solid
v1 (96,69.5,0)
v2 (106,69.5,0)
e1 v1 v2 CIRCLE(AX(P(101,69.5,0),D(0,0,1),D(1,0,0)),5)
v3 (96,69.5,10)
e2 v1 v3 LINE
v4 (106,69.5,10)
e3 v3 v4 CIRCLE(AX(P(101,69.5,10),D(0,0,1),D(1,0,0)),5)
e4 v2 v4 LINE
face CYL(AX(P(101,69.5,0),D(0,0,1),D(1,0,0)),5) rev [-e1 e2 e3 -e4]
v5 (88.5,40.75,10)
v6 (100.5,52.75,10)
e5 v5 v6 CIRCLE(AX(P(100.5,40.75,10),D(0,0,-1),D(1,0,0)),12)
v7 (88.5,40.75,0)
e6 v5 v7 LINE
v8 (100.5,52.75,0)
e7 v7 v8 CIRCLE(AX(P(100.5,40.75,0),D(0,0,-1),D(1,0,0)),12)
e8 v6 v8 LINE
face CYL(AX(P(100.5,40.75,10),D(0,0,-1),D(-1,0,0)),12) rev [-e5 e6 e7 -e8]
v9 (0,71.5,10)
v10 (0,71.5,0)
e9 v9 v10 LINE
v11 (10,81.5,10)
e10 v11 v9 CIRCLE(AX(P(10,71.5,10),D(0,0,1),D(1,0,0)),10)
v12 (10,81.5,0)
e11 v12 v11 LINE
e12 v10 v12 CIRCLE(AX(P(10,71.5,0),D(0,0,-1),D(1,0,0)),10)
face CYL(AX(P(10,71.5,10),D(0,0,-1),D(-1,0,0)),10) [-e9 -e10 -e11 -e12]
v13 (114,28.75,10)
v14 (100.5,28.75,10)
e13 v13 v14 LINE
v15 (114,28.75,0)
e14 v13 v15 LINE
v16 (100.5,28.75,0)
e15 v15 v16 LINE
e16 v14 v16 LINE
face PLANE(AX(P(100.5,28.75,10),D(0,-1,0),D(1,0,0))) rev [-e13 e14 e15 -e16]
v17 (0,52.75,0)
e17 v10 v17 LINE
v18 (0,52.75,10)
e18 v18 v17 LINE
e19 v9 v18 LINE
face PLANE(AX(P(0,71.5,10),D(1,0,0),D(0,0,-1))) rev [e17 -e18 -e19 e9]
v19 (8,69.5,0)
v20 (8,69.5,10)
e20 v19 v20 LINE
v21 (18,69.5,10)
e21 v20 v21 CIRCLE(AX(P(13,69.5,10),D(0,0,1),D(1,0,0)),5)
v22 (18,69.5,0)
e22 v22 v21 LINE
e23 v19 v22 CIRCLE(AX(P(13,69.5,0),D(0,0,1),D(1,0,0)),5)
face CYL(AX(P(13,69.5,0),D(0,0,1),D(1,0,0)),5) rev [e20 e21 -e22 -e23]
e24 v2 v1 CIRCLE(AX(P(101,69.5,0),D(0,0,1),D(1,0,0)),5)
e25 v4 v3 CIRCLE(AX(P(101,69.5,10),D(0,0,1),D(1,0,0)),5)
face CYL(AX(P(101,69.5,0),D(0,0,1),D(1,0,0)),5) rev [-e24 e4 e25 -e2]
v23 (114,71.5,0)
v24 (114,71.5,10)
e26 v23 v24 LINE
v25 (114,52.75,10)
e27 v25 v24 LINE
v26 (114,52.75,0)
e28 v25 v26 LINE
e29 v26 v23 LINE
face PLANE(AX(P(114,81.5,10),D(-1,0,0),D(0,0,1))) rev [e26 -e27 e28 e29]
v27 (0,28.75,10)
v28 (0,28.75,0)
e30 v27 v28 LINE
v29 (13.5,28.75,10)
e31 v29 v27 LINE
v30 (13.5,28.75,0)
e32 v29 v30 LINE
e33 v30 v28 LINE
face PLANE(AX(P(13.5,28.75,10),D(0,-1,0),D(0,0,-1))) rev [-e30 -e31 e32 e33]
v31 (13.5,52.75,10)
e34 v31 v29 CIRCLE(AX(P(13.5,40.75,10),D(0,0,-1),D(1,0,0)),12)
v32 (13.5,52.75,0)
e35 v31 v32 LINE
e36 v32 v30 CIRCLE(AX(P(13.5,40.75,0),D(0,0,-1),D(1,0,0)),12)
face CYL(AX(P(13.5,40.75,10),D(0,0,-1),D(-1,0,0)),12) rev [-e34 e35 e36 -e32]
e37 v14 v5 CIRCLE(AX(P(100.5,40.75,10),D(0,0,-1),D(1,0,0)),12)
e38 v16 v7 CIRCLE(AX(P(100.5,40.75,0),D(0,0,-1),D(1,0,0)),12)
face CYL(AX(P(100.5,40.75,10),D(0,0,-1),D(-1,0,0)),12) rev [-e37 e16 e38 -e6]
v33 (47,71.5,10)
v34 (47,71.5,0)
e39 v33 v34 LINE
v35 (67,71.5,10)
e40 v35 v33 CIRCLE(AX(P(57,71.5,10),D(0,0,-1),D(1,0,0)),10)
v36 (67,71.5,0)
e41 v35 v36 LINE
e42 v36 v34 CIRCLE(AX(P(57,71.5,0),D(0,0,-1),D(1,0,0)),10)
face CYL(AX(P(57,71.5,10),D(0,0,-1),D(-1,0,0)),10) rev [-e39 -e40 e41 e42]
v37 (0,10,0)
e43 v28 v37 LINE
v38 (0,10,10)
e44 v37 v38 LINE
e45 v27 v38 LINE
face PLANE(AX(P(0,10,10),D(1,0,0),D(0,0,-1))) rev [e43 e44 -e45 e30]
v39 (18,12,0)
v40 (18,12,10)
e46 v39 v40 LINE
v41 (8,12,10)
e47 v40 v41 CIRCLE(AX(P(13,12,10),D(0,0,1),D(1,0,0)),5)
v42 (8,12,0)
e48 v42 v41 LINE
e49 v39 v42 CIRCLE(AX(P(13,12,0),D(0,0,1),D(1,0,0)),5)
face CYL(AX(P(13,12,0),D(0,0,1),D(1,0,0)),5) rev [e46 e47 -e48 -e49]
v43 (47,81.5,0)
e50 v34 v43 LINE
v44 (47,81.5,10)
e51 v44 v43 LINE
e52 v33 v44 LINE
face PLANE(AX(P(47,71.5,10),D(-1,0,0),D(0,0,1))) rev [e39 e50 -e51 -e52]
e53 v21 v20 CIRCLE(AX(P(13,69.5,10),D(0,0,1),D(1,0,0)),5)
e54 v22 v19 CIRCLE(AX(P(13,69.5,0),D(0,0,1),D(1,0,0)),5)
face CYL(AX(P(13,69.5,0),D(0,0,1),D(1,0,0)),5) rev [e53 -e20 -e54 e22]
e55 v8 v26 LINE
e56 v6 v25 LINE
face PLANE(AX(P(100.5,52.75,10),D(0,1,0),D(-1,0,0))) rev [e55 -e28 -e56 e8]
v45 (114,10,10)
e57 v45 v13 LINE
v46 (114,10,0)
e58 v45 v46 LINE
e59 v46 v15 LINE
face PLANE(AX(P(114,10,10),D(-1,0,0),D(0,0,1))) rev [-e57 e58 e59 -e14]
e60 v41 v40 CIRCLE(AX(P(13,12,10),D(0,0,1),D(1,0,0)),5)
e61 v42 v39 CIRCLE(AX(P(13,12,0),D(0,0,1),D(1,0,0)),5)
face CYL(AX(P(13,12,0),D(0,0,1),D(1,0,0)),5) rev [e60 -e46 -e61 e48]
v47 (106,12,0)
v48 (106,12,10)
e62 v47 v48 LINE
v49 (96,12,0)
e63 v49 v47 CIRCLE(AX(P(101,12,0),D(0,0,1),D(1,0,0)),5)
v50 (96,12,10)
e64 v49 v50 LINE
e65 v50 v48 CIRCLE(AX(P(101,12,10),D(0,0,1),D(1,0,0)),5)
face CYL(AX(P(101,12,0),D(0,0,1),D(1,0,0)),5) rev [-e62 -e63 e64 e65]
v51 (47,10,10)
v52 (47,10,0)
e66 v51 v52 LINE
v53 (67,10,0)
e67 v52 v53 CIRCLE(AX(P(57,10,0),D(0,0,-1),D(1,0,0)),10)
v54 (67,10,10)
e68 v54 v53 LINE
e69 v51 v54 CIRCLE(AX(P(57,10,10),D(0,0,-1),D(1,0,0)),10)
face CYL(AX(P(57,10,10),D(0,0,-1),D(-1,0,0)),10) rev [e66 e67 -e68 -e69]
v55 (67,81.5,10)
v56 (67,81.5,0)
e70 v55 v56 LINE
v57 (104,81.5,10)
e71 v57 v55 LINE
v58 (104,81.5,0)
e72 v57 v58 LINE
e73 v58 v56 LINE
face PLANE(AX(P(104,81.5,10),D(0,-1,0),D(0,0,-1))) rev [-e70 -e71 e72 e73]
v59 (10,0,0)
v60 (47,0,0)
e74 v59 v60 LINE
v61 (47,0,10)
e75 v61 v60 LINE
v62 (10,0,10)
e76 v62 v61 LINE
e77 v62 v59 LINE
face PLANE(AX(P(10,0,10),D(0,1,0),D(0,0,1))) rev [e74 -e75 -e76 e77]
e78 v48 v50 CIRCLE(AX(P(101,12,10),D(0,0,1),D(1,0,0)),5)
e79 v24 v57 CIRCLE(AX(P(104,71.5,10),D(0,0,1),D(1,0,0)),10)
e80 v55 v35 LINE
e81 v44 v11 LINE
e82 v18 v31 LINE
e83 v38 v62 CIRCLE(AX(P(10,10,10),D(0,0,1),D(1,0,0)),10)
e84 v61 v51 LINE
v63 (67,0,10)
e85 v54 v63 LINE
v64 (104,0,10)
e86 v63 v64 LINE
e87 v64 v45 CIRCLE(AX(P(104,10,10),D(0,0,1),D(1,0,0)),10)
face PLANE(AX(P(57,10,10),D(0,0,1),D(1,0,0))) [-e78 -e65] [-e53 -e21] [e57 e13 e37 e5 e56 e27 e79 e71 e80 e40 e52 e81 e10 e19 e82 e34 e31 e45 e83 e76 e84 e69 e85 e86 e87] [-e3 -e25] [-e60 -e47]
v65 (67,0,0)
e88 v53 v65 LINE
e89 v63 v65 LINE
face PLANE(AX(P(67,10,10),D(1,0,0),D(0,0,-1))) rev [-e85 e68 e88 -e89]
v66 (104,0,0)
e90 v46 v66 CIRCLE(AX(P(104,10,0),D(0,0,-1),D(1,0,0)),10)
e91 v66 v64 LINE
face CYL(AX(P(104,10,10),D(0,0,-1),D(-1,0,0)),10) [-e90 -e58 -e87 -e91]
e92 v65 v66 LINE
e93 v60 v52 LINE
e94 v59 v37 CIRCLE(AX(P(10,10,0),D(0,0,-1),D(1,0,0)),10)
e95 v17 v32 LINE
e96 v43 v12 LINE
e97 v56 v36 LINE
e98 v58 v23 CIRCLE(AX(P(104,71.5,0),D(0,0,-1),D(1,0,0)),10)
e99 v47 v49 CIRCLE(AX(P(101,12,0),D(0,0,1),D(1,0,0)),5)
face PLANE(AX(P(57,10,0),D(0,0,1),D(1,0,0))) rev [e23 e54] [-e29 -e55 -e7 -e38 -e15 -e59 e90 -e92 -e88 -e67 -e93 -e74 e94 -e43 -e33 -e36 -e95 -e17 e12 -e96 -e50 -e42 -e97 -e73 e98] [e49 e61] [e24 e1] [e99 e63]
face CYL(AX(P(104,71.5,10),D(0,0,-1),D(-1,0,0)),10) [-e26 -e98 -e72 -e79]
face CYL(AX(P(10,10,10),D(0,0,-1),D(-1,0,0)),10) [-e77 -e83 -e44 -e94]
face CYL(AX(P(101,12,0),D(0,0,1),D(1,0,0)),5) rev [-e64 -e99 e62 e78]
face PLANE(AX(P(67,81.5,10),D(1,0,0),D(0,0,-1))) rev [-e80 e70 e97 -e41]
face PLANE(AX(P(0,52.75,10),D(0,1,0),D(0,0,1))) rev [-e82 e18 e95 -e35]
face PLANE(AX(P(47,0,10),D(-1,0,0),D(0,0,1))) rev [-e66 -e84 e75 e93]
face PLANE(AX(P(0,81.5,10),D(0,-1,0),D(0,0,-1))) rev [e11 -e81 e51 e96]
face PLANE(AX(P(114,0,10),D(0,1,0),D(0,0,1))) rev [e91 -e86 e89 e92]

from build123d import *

# Parameters (mm, degrees)
BRACKET_PLATE_DEPTH        = 10
MOUNTING_HOLES_SKETCH_R    = 5
MOUNTING_HOLES_4X_10_DEPTH = 141.492882382
CORNER_FILLETS_R10_R       = 10


with BuildPart() as part:
    # Bracket Profile Sketch → Bracket Plate (new body)
    with BuildSketch(Plane.XY):
        with BuildLine():
            Line((10, 0), (47, 0))
            Line((47, 0), (47, 10))
            ThreePointArc((47, 10), (57, 20), (67, 10))
            Line((67, 10), (67, 0))
            Line((67, 0), (104, 0))
            Line((104, 0), (114, 0))
            Line((114, 0), (114, 10))
            Line((114, 10), (114, 28.75))
            Line((114, 28.75), (100.5, 28.75))
            ThreePointArc((100.5, 28.75), (88.5, 40.75), (100.5, 52.75))
            Line((100.5, 52.75), (114, 52.75))
            Line((114, 52.75), (114, 71.5))
            Line((114, 71.5), (114, 81.5))
            Line((114, 81.5), (104, 81.5))
            Line((104, 81.5), (67, 81.5))
            Line((67, 81.5), (67, 71.5))
            ThreePointArc((67, 71.5), (57, 61.5), (47, 71.5))
            Line((47, 71.5), (47, 81.5))
            Line((47, 81.5), (10, 81.5))
            Line((10, 81.5), (0, 81.5))
            Line((0, 81.5), (0, 71.5))
            Line((0, 71.5), (0, 52.75))
            Line((0, 52.75), (13.5, 52.75))
            ThreePointArc((13.5, 52.75), (25.5, 40.75), (13.5, 28.75))
            Line((13.5, 28.75), (0, 28.75))
            Line((0, 28.75), (0, 10))
            Line((0, 10), (0, 0))
            Line((0, 0), (10, 0))
        make_face()
    extrude(amount=BRACKET_PLATE_DEPTH)

    # Mounting Holes Sketch → Mounting Holes 4xØ10 (cut, through all)
    with BuildSketch(Plane.XY.offset(10)):
        with Locations((13, 69.5)):
            Circle(MOUNTING_HOLES_SKETCH_R)
        with Locations((101, 69.5)):
            Circle(MOUNTING_HOLES_SKETCH_R)
        with Locations((101, 12)):
            Circle(MOUNTING_HOLES_SKETCH_R)
        with Locations((13, 12)):
            Circle(MOUNTING_HOLES_SKETCH_R)
    extrude(amount=-MOUNTING_HOLES_4X_10_DEPTH, mode=Mode.SUBTRACT)

    # Corner Fillets R10
    corner_fillets_r10_edges = [part.edges().sort_by_distance(p)[0] for p in [
        (0, 0, 5),
        (0, 81.5, 5),
        (114, 81.5, 5),
        (114, 0, 5),
    ]]
    fillet(corner_fillets_r10_edges, radius=CORNER_FILLETS_R10_R)


solid = part.part
